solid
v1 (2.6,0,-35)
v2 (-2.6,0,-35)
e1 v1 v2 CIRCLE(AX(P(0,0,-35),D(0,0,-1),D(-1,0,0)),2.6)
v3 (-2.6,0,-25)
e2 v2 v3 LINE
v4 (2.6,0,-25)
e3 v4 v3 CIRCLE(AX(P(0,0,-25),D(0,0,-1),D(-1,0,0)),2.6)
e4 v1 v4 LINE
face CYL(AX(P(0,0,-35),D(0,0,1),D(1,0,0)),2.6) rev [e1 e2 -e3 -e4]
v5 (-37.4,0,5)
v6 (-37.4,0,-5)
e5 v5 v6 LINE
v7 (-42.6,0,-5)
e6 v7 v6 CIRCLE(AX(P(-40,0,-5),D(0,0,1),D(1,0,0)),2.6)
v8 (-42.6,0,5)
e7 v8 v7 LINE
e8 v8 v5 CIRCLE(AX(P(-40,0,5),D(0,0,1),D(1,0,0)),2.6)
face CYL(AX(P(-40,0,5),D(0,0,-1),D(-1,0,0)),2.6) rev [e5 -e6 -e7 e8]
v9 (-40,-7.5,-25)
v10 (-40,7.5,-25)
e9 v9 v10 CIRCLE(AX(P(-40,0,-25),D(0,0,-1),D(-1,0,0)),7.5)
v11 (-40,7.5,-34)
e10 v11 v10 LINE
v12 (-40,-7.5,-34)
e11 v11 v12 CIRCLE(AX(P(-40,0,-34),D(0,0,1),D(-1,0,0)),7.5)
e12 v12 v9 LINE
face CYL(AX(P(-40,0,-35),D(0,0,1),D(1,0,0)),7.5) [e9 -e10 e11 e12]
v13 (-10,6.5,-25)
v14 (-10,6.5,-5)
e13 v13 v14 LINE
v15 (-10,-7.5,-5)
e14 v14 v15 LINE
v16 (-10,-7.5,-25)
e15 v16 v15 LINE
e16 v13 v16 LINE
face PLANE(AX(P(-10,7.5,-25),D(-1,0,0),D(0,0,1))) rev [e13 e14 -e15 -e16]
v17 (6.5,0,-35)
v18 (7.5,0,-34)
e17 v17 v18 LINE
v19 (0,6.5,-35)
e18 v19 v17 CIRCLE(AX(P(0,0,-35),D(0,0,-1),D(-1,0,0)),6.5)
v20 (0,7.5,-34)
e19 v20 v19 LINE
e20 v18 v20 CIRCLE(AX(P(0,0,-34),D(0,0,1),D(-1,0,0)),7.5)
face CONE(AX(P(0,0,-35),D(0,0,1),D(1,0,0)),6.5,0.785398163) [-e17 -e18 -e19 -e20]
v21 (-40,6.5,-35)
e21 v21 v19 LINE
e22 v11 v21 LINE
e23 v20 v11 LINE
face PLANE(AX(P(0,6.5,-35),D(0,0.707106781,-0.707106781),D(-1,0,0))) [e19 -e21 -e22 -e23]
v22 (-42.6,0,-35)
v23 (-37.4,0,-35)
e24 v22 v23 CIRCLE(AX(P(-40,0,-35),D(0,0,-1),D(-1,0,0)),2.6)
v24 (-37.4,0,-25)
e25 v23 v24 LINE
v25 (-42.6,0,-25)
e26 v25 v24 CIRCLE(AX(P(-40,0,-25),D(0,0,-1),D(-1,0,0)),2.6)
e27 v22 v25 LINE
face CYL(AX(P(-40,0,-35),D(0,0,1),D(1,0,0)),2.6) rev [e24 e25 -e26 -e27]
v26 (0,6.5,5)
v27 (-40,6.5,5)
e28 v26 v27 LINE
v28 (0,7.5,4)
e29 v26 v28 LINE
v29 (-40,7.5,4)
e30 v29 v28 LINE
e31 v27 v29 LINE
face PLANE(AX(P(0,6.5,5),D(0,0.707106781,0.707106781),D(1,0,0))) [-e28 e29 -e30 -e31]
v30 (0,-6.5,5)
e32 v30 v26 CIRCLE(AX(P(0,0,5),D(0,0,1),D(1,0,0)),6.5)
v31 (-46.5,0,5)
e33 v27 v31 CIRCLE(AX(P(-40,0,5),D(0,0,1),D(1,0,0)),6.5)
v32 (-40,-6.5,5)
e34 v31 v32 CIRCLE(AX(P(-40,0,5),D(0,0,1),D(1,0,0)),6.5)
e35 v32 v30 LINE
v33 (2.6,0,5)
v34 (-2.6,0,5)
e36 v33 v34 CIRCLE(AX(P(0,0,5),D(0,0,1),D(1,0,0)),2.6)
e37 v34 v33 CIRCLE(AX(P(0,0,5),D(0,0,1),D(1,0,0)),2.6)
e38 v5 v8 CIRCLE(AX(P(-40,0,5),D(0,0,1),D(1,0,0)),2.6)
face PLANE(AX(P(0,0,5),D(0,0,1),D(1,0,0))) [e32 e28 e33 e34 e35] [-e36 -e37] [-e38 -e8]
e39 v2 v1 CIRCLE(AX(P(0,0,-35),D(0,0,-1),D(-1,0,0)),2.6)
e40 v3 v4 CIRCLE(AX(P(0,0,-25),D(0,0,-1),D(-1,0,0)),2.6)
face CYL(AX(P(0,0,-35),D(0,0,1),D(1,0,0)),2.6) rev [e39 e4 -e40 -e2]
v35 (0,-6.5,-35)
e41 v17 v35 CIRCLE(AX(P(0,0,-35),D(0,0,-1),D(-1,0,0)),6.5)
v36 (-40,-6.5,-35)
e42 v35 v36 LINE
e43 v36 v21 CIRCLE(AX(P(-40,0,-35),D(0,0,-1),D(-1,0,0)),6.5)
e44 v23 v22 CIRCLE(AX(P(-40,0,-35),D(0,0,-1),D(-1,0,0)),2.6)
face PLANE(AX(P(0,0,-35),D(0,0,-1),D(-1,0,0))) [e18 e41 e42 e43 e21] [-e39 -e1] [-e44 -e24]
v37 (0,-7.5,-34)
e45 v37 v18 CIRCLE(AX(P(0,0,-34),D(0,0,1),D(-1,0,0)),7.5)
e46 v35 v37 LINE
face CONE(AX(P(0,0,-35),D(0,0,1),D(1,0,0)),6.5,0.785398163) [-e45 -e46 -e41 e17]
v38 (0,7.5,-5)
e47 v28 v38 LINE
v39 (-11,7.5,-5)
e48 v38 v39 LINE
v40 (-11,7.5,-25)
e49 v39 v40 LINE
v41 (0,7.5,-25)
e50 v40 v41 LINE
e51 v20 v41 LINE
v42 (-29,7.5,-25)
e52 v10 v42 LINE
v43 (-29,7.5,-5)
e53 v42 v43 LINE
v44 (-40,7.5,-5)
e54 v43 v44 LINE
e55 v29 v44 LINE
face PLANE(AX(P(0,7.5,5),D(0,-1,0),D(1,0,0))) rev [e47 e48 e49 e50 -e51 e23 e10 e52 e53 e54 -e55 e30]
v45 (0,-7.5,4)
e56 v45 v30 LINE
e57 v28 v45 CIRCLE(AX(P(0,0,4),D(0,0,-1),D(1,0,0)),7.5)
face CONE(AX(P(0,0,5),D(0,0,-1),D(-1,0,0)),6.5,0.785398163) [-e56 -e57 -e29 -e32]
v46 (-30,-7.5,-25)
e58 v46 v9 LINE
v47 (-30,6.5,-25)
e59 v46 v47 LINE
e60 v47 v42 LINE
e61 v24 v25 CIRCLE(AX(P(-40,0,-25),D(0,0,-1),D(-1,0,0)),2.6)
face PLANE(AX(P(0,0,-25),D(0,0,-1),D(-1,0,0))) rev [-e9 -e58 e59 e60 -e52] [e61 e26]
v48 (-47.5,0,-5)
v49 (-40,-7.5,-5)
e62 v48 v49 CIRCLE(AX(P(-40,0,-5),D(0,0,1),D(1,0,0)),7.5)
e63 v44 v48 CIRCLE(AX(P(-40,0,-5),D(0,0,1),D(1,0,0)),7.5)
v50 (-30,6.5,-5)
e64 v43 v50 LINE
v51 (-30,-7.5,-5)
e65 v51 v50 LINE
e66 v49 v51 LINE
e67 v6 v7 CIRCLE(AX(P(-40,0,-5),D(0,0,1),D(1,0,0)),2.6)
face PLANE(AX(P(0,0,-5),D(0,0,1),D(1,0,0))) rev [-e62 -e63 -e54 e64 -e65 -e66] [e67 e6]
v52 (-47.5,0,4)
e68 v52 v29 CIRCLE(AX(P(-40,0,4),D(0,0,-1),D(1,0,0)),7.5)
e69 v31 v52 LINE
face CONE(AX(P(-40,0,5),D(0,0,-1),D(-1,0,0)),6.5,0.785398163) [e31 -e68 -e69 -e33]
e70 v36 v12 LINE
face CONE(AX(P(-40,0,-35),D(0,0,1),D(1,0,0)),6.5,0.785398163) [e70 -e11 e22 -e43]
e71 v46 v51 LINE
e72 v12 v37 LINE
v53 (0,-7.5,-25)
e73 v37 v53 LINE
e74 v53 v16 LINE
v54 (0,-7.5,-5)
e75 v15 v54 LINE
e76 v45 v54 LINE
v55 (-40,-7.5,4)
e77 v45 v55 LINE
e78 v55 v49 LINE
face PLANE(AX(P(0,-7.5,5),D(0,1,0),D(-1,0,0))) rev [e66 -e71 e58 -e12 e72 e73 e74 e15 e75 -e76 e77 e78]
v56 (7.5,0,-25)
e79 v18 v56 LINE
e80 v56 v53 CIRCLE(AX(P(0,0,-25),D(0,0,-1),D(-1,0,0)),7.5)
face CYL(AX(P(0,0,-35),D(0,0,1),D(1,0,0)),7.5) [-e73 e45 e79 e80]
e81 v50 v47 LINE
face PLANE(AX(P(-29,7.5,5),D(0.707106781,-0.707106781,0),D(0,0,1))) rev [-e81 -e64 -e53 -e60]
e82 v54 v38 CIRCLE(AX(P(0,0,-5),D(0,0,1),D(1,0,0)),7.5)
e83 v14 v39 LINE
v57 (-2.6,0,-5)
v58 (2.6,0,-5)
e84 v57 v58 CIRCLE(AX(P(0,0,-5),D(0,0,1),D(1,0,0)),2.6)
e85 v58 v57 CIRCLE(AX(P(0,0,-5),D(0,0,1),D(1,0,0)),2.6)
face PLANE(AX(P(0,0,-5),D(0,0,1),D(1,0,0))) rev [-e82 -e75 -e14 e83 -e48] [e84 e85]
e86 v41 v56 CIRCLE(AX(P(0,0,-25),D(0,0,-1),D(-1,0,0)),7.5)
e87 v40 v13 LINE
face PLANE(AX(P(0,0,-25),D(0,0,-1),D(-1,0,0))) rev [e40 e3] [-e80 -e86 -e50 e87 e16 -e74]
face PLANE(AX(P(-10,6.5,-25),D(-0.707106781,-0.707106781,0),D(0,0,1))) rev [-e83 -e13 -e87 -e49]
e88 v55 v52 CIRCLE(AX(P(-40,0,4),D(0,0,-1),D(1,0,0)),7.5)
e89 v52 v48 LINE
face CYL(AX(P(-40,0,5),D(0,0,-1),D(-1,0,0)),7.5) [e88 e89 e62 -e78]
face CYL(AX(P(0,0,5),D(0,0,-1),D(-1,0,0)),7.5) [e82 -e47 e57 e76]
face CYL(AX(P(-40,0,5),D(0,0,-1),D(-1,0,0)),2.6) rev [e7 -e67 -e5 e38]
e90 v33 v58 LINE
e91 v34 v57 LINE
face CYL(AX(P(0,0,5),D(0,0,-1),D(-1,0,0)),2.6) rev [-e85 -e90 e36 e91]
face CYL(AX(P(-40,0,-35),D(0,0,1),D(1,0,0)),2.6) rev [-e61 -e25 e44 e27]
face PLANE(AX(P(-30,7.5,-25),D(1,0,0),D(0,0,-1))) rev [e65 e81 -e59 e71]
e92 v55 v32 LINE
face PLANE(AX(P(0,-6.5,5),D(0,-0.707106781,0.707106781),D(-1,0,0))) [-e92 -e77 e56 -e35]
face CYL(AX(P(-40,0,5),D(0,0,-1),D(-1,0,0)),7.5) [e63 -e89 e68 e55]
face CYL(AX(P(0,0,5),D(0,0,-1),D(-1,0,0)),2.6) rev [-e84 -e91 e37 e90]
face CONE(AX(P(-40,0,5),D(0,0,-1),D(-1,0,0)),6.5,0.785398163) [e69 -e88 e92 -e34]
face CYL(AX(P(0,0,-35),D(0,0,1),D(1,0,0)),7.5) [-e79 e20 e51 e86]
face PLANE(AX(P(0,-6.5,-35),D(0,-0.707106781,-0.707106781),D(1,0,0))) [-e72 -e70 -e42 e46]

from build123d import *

# Parameters (mm, degrees)
SKETCH1_R           = 2.6
BOSS_EXTRUDE1_DEPTH = 5
SKETCH2_W           = 20
SKETCH2_H           = 15
BOSS_EXTRUDE2_DEPTH = 20
SKETCH3_R           = 2.6
BOSS_EXTRUDE3_DEPTH = 10
CHAMFER1_SIZE       = 1


with BuildPart() as part:
    # Sketch1 → Boss-Extrude1 (new, symmetric)
    with BuildSketch(Plane.XY):
        with BuildLine():
            Line((0, -7.5), (-40, -7.5))
            ThreePointArc((-40, -7.5), (-47.5, 0), (-40, 7.5))
            Line((-40, 7.5), (0, 7.5))
            ThreePointArc((0, 7.5), (7.5, 0), (0, -7.5))
        make_face()
        Circle(SKETCH1_R, mode=Mode.SUBTRACT)
        with Locations((-40, 0)):
            Circle(SKETCH1_R, mode=Mode.SUBTRACT)
    extrude(amount=BOSS_EXTRUDE1_DEPTH, both=True)

    # Sketch2 → Boss-Extrude2 (add)
    with BuildSketch(Plane(origin=(0, 0, -5), x_dir=(-1, 0, 0), z_dir=(0, 0, -1))):
        with Locations((20, 0)):
            Rectangle(SKETCH2_W, SKETCH2_H)
    extrude(amount=BOSS_EXTRUDE2_DEPTH)

    # Sketch3 → Boss-Extrude3 (add)
    with BuildSketch(Plane(origin=(0, 0, -25), x_dir=(-1, 0, 0), z_dir=(0, 0, -1))):
        with BuildLine():
            Line((0, 7.5), (40, 7.5))
            ThreePointArc((40, 7.5), (47.5, 0), (40, -7.5))
            Line((40, -7.5), (0, -7.5))
            ThreePointArc((0, -7.5), (-7.5, 0), (0, 7.5))
        make_face()
        with Locations(Location((0, 0, 0), (0, 0, 180))):
            Circle(SKETCH3_R, mode=Mode.SUBTRACT)
        with Locations(Location((40, 0, 0), (0, 0, 180))):
            Circle(SKETCH3_R, mode=Mode.SUBTRACT)
    extrude(amount=BOSS_EXTRUDE3_DEPTH)

    # Chamfer1
    chamfer1_edges = [part.edges().sort_by_distance(p)[0] for p in [
        (-47.5, 0, 5),
        (-20, -7.5, 5),
        (-30, 7.5, -15),
        (-10, 7.5, -15),
        (7.5, 0, -35),
        (-20, -7.5, -35),
        (-47.5, 0, -35),
        (-20, 7.5, -35),
        (7.5, 0, 5),
        (-20, 7.5, 5),
    ]]
    chamfer(chamfer1_edges, length=CHAMFER1_SIZE)


solid = part.part
